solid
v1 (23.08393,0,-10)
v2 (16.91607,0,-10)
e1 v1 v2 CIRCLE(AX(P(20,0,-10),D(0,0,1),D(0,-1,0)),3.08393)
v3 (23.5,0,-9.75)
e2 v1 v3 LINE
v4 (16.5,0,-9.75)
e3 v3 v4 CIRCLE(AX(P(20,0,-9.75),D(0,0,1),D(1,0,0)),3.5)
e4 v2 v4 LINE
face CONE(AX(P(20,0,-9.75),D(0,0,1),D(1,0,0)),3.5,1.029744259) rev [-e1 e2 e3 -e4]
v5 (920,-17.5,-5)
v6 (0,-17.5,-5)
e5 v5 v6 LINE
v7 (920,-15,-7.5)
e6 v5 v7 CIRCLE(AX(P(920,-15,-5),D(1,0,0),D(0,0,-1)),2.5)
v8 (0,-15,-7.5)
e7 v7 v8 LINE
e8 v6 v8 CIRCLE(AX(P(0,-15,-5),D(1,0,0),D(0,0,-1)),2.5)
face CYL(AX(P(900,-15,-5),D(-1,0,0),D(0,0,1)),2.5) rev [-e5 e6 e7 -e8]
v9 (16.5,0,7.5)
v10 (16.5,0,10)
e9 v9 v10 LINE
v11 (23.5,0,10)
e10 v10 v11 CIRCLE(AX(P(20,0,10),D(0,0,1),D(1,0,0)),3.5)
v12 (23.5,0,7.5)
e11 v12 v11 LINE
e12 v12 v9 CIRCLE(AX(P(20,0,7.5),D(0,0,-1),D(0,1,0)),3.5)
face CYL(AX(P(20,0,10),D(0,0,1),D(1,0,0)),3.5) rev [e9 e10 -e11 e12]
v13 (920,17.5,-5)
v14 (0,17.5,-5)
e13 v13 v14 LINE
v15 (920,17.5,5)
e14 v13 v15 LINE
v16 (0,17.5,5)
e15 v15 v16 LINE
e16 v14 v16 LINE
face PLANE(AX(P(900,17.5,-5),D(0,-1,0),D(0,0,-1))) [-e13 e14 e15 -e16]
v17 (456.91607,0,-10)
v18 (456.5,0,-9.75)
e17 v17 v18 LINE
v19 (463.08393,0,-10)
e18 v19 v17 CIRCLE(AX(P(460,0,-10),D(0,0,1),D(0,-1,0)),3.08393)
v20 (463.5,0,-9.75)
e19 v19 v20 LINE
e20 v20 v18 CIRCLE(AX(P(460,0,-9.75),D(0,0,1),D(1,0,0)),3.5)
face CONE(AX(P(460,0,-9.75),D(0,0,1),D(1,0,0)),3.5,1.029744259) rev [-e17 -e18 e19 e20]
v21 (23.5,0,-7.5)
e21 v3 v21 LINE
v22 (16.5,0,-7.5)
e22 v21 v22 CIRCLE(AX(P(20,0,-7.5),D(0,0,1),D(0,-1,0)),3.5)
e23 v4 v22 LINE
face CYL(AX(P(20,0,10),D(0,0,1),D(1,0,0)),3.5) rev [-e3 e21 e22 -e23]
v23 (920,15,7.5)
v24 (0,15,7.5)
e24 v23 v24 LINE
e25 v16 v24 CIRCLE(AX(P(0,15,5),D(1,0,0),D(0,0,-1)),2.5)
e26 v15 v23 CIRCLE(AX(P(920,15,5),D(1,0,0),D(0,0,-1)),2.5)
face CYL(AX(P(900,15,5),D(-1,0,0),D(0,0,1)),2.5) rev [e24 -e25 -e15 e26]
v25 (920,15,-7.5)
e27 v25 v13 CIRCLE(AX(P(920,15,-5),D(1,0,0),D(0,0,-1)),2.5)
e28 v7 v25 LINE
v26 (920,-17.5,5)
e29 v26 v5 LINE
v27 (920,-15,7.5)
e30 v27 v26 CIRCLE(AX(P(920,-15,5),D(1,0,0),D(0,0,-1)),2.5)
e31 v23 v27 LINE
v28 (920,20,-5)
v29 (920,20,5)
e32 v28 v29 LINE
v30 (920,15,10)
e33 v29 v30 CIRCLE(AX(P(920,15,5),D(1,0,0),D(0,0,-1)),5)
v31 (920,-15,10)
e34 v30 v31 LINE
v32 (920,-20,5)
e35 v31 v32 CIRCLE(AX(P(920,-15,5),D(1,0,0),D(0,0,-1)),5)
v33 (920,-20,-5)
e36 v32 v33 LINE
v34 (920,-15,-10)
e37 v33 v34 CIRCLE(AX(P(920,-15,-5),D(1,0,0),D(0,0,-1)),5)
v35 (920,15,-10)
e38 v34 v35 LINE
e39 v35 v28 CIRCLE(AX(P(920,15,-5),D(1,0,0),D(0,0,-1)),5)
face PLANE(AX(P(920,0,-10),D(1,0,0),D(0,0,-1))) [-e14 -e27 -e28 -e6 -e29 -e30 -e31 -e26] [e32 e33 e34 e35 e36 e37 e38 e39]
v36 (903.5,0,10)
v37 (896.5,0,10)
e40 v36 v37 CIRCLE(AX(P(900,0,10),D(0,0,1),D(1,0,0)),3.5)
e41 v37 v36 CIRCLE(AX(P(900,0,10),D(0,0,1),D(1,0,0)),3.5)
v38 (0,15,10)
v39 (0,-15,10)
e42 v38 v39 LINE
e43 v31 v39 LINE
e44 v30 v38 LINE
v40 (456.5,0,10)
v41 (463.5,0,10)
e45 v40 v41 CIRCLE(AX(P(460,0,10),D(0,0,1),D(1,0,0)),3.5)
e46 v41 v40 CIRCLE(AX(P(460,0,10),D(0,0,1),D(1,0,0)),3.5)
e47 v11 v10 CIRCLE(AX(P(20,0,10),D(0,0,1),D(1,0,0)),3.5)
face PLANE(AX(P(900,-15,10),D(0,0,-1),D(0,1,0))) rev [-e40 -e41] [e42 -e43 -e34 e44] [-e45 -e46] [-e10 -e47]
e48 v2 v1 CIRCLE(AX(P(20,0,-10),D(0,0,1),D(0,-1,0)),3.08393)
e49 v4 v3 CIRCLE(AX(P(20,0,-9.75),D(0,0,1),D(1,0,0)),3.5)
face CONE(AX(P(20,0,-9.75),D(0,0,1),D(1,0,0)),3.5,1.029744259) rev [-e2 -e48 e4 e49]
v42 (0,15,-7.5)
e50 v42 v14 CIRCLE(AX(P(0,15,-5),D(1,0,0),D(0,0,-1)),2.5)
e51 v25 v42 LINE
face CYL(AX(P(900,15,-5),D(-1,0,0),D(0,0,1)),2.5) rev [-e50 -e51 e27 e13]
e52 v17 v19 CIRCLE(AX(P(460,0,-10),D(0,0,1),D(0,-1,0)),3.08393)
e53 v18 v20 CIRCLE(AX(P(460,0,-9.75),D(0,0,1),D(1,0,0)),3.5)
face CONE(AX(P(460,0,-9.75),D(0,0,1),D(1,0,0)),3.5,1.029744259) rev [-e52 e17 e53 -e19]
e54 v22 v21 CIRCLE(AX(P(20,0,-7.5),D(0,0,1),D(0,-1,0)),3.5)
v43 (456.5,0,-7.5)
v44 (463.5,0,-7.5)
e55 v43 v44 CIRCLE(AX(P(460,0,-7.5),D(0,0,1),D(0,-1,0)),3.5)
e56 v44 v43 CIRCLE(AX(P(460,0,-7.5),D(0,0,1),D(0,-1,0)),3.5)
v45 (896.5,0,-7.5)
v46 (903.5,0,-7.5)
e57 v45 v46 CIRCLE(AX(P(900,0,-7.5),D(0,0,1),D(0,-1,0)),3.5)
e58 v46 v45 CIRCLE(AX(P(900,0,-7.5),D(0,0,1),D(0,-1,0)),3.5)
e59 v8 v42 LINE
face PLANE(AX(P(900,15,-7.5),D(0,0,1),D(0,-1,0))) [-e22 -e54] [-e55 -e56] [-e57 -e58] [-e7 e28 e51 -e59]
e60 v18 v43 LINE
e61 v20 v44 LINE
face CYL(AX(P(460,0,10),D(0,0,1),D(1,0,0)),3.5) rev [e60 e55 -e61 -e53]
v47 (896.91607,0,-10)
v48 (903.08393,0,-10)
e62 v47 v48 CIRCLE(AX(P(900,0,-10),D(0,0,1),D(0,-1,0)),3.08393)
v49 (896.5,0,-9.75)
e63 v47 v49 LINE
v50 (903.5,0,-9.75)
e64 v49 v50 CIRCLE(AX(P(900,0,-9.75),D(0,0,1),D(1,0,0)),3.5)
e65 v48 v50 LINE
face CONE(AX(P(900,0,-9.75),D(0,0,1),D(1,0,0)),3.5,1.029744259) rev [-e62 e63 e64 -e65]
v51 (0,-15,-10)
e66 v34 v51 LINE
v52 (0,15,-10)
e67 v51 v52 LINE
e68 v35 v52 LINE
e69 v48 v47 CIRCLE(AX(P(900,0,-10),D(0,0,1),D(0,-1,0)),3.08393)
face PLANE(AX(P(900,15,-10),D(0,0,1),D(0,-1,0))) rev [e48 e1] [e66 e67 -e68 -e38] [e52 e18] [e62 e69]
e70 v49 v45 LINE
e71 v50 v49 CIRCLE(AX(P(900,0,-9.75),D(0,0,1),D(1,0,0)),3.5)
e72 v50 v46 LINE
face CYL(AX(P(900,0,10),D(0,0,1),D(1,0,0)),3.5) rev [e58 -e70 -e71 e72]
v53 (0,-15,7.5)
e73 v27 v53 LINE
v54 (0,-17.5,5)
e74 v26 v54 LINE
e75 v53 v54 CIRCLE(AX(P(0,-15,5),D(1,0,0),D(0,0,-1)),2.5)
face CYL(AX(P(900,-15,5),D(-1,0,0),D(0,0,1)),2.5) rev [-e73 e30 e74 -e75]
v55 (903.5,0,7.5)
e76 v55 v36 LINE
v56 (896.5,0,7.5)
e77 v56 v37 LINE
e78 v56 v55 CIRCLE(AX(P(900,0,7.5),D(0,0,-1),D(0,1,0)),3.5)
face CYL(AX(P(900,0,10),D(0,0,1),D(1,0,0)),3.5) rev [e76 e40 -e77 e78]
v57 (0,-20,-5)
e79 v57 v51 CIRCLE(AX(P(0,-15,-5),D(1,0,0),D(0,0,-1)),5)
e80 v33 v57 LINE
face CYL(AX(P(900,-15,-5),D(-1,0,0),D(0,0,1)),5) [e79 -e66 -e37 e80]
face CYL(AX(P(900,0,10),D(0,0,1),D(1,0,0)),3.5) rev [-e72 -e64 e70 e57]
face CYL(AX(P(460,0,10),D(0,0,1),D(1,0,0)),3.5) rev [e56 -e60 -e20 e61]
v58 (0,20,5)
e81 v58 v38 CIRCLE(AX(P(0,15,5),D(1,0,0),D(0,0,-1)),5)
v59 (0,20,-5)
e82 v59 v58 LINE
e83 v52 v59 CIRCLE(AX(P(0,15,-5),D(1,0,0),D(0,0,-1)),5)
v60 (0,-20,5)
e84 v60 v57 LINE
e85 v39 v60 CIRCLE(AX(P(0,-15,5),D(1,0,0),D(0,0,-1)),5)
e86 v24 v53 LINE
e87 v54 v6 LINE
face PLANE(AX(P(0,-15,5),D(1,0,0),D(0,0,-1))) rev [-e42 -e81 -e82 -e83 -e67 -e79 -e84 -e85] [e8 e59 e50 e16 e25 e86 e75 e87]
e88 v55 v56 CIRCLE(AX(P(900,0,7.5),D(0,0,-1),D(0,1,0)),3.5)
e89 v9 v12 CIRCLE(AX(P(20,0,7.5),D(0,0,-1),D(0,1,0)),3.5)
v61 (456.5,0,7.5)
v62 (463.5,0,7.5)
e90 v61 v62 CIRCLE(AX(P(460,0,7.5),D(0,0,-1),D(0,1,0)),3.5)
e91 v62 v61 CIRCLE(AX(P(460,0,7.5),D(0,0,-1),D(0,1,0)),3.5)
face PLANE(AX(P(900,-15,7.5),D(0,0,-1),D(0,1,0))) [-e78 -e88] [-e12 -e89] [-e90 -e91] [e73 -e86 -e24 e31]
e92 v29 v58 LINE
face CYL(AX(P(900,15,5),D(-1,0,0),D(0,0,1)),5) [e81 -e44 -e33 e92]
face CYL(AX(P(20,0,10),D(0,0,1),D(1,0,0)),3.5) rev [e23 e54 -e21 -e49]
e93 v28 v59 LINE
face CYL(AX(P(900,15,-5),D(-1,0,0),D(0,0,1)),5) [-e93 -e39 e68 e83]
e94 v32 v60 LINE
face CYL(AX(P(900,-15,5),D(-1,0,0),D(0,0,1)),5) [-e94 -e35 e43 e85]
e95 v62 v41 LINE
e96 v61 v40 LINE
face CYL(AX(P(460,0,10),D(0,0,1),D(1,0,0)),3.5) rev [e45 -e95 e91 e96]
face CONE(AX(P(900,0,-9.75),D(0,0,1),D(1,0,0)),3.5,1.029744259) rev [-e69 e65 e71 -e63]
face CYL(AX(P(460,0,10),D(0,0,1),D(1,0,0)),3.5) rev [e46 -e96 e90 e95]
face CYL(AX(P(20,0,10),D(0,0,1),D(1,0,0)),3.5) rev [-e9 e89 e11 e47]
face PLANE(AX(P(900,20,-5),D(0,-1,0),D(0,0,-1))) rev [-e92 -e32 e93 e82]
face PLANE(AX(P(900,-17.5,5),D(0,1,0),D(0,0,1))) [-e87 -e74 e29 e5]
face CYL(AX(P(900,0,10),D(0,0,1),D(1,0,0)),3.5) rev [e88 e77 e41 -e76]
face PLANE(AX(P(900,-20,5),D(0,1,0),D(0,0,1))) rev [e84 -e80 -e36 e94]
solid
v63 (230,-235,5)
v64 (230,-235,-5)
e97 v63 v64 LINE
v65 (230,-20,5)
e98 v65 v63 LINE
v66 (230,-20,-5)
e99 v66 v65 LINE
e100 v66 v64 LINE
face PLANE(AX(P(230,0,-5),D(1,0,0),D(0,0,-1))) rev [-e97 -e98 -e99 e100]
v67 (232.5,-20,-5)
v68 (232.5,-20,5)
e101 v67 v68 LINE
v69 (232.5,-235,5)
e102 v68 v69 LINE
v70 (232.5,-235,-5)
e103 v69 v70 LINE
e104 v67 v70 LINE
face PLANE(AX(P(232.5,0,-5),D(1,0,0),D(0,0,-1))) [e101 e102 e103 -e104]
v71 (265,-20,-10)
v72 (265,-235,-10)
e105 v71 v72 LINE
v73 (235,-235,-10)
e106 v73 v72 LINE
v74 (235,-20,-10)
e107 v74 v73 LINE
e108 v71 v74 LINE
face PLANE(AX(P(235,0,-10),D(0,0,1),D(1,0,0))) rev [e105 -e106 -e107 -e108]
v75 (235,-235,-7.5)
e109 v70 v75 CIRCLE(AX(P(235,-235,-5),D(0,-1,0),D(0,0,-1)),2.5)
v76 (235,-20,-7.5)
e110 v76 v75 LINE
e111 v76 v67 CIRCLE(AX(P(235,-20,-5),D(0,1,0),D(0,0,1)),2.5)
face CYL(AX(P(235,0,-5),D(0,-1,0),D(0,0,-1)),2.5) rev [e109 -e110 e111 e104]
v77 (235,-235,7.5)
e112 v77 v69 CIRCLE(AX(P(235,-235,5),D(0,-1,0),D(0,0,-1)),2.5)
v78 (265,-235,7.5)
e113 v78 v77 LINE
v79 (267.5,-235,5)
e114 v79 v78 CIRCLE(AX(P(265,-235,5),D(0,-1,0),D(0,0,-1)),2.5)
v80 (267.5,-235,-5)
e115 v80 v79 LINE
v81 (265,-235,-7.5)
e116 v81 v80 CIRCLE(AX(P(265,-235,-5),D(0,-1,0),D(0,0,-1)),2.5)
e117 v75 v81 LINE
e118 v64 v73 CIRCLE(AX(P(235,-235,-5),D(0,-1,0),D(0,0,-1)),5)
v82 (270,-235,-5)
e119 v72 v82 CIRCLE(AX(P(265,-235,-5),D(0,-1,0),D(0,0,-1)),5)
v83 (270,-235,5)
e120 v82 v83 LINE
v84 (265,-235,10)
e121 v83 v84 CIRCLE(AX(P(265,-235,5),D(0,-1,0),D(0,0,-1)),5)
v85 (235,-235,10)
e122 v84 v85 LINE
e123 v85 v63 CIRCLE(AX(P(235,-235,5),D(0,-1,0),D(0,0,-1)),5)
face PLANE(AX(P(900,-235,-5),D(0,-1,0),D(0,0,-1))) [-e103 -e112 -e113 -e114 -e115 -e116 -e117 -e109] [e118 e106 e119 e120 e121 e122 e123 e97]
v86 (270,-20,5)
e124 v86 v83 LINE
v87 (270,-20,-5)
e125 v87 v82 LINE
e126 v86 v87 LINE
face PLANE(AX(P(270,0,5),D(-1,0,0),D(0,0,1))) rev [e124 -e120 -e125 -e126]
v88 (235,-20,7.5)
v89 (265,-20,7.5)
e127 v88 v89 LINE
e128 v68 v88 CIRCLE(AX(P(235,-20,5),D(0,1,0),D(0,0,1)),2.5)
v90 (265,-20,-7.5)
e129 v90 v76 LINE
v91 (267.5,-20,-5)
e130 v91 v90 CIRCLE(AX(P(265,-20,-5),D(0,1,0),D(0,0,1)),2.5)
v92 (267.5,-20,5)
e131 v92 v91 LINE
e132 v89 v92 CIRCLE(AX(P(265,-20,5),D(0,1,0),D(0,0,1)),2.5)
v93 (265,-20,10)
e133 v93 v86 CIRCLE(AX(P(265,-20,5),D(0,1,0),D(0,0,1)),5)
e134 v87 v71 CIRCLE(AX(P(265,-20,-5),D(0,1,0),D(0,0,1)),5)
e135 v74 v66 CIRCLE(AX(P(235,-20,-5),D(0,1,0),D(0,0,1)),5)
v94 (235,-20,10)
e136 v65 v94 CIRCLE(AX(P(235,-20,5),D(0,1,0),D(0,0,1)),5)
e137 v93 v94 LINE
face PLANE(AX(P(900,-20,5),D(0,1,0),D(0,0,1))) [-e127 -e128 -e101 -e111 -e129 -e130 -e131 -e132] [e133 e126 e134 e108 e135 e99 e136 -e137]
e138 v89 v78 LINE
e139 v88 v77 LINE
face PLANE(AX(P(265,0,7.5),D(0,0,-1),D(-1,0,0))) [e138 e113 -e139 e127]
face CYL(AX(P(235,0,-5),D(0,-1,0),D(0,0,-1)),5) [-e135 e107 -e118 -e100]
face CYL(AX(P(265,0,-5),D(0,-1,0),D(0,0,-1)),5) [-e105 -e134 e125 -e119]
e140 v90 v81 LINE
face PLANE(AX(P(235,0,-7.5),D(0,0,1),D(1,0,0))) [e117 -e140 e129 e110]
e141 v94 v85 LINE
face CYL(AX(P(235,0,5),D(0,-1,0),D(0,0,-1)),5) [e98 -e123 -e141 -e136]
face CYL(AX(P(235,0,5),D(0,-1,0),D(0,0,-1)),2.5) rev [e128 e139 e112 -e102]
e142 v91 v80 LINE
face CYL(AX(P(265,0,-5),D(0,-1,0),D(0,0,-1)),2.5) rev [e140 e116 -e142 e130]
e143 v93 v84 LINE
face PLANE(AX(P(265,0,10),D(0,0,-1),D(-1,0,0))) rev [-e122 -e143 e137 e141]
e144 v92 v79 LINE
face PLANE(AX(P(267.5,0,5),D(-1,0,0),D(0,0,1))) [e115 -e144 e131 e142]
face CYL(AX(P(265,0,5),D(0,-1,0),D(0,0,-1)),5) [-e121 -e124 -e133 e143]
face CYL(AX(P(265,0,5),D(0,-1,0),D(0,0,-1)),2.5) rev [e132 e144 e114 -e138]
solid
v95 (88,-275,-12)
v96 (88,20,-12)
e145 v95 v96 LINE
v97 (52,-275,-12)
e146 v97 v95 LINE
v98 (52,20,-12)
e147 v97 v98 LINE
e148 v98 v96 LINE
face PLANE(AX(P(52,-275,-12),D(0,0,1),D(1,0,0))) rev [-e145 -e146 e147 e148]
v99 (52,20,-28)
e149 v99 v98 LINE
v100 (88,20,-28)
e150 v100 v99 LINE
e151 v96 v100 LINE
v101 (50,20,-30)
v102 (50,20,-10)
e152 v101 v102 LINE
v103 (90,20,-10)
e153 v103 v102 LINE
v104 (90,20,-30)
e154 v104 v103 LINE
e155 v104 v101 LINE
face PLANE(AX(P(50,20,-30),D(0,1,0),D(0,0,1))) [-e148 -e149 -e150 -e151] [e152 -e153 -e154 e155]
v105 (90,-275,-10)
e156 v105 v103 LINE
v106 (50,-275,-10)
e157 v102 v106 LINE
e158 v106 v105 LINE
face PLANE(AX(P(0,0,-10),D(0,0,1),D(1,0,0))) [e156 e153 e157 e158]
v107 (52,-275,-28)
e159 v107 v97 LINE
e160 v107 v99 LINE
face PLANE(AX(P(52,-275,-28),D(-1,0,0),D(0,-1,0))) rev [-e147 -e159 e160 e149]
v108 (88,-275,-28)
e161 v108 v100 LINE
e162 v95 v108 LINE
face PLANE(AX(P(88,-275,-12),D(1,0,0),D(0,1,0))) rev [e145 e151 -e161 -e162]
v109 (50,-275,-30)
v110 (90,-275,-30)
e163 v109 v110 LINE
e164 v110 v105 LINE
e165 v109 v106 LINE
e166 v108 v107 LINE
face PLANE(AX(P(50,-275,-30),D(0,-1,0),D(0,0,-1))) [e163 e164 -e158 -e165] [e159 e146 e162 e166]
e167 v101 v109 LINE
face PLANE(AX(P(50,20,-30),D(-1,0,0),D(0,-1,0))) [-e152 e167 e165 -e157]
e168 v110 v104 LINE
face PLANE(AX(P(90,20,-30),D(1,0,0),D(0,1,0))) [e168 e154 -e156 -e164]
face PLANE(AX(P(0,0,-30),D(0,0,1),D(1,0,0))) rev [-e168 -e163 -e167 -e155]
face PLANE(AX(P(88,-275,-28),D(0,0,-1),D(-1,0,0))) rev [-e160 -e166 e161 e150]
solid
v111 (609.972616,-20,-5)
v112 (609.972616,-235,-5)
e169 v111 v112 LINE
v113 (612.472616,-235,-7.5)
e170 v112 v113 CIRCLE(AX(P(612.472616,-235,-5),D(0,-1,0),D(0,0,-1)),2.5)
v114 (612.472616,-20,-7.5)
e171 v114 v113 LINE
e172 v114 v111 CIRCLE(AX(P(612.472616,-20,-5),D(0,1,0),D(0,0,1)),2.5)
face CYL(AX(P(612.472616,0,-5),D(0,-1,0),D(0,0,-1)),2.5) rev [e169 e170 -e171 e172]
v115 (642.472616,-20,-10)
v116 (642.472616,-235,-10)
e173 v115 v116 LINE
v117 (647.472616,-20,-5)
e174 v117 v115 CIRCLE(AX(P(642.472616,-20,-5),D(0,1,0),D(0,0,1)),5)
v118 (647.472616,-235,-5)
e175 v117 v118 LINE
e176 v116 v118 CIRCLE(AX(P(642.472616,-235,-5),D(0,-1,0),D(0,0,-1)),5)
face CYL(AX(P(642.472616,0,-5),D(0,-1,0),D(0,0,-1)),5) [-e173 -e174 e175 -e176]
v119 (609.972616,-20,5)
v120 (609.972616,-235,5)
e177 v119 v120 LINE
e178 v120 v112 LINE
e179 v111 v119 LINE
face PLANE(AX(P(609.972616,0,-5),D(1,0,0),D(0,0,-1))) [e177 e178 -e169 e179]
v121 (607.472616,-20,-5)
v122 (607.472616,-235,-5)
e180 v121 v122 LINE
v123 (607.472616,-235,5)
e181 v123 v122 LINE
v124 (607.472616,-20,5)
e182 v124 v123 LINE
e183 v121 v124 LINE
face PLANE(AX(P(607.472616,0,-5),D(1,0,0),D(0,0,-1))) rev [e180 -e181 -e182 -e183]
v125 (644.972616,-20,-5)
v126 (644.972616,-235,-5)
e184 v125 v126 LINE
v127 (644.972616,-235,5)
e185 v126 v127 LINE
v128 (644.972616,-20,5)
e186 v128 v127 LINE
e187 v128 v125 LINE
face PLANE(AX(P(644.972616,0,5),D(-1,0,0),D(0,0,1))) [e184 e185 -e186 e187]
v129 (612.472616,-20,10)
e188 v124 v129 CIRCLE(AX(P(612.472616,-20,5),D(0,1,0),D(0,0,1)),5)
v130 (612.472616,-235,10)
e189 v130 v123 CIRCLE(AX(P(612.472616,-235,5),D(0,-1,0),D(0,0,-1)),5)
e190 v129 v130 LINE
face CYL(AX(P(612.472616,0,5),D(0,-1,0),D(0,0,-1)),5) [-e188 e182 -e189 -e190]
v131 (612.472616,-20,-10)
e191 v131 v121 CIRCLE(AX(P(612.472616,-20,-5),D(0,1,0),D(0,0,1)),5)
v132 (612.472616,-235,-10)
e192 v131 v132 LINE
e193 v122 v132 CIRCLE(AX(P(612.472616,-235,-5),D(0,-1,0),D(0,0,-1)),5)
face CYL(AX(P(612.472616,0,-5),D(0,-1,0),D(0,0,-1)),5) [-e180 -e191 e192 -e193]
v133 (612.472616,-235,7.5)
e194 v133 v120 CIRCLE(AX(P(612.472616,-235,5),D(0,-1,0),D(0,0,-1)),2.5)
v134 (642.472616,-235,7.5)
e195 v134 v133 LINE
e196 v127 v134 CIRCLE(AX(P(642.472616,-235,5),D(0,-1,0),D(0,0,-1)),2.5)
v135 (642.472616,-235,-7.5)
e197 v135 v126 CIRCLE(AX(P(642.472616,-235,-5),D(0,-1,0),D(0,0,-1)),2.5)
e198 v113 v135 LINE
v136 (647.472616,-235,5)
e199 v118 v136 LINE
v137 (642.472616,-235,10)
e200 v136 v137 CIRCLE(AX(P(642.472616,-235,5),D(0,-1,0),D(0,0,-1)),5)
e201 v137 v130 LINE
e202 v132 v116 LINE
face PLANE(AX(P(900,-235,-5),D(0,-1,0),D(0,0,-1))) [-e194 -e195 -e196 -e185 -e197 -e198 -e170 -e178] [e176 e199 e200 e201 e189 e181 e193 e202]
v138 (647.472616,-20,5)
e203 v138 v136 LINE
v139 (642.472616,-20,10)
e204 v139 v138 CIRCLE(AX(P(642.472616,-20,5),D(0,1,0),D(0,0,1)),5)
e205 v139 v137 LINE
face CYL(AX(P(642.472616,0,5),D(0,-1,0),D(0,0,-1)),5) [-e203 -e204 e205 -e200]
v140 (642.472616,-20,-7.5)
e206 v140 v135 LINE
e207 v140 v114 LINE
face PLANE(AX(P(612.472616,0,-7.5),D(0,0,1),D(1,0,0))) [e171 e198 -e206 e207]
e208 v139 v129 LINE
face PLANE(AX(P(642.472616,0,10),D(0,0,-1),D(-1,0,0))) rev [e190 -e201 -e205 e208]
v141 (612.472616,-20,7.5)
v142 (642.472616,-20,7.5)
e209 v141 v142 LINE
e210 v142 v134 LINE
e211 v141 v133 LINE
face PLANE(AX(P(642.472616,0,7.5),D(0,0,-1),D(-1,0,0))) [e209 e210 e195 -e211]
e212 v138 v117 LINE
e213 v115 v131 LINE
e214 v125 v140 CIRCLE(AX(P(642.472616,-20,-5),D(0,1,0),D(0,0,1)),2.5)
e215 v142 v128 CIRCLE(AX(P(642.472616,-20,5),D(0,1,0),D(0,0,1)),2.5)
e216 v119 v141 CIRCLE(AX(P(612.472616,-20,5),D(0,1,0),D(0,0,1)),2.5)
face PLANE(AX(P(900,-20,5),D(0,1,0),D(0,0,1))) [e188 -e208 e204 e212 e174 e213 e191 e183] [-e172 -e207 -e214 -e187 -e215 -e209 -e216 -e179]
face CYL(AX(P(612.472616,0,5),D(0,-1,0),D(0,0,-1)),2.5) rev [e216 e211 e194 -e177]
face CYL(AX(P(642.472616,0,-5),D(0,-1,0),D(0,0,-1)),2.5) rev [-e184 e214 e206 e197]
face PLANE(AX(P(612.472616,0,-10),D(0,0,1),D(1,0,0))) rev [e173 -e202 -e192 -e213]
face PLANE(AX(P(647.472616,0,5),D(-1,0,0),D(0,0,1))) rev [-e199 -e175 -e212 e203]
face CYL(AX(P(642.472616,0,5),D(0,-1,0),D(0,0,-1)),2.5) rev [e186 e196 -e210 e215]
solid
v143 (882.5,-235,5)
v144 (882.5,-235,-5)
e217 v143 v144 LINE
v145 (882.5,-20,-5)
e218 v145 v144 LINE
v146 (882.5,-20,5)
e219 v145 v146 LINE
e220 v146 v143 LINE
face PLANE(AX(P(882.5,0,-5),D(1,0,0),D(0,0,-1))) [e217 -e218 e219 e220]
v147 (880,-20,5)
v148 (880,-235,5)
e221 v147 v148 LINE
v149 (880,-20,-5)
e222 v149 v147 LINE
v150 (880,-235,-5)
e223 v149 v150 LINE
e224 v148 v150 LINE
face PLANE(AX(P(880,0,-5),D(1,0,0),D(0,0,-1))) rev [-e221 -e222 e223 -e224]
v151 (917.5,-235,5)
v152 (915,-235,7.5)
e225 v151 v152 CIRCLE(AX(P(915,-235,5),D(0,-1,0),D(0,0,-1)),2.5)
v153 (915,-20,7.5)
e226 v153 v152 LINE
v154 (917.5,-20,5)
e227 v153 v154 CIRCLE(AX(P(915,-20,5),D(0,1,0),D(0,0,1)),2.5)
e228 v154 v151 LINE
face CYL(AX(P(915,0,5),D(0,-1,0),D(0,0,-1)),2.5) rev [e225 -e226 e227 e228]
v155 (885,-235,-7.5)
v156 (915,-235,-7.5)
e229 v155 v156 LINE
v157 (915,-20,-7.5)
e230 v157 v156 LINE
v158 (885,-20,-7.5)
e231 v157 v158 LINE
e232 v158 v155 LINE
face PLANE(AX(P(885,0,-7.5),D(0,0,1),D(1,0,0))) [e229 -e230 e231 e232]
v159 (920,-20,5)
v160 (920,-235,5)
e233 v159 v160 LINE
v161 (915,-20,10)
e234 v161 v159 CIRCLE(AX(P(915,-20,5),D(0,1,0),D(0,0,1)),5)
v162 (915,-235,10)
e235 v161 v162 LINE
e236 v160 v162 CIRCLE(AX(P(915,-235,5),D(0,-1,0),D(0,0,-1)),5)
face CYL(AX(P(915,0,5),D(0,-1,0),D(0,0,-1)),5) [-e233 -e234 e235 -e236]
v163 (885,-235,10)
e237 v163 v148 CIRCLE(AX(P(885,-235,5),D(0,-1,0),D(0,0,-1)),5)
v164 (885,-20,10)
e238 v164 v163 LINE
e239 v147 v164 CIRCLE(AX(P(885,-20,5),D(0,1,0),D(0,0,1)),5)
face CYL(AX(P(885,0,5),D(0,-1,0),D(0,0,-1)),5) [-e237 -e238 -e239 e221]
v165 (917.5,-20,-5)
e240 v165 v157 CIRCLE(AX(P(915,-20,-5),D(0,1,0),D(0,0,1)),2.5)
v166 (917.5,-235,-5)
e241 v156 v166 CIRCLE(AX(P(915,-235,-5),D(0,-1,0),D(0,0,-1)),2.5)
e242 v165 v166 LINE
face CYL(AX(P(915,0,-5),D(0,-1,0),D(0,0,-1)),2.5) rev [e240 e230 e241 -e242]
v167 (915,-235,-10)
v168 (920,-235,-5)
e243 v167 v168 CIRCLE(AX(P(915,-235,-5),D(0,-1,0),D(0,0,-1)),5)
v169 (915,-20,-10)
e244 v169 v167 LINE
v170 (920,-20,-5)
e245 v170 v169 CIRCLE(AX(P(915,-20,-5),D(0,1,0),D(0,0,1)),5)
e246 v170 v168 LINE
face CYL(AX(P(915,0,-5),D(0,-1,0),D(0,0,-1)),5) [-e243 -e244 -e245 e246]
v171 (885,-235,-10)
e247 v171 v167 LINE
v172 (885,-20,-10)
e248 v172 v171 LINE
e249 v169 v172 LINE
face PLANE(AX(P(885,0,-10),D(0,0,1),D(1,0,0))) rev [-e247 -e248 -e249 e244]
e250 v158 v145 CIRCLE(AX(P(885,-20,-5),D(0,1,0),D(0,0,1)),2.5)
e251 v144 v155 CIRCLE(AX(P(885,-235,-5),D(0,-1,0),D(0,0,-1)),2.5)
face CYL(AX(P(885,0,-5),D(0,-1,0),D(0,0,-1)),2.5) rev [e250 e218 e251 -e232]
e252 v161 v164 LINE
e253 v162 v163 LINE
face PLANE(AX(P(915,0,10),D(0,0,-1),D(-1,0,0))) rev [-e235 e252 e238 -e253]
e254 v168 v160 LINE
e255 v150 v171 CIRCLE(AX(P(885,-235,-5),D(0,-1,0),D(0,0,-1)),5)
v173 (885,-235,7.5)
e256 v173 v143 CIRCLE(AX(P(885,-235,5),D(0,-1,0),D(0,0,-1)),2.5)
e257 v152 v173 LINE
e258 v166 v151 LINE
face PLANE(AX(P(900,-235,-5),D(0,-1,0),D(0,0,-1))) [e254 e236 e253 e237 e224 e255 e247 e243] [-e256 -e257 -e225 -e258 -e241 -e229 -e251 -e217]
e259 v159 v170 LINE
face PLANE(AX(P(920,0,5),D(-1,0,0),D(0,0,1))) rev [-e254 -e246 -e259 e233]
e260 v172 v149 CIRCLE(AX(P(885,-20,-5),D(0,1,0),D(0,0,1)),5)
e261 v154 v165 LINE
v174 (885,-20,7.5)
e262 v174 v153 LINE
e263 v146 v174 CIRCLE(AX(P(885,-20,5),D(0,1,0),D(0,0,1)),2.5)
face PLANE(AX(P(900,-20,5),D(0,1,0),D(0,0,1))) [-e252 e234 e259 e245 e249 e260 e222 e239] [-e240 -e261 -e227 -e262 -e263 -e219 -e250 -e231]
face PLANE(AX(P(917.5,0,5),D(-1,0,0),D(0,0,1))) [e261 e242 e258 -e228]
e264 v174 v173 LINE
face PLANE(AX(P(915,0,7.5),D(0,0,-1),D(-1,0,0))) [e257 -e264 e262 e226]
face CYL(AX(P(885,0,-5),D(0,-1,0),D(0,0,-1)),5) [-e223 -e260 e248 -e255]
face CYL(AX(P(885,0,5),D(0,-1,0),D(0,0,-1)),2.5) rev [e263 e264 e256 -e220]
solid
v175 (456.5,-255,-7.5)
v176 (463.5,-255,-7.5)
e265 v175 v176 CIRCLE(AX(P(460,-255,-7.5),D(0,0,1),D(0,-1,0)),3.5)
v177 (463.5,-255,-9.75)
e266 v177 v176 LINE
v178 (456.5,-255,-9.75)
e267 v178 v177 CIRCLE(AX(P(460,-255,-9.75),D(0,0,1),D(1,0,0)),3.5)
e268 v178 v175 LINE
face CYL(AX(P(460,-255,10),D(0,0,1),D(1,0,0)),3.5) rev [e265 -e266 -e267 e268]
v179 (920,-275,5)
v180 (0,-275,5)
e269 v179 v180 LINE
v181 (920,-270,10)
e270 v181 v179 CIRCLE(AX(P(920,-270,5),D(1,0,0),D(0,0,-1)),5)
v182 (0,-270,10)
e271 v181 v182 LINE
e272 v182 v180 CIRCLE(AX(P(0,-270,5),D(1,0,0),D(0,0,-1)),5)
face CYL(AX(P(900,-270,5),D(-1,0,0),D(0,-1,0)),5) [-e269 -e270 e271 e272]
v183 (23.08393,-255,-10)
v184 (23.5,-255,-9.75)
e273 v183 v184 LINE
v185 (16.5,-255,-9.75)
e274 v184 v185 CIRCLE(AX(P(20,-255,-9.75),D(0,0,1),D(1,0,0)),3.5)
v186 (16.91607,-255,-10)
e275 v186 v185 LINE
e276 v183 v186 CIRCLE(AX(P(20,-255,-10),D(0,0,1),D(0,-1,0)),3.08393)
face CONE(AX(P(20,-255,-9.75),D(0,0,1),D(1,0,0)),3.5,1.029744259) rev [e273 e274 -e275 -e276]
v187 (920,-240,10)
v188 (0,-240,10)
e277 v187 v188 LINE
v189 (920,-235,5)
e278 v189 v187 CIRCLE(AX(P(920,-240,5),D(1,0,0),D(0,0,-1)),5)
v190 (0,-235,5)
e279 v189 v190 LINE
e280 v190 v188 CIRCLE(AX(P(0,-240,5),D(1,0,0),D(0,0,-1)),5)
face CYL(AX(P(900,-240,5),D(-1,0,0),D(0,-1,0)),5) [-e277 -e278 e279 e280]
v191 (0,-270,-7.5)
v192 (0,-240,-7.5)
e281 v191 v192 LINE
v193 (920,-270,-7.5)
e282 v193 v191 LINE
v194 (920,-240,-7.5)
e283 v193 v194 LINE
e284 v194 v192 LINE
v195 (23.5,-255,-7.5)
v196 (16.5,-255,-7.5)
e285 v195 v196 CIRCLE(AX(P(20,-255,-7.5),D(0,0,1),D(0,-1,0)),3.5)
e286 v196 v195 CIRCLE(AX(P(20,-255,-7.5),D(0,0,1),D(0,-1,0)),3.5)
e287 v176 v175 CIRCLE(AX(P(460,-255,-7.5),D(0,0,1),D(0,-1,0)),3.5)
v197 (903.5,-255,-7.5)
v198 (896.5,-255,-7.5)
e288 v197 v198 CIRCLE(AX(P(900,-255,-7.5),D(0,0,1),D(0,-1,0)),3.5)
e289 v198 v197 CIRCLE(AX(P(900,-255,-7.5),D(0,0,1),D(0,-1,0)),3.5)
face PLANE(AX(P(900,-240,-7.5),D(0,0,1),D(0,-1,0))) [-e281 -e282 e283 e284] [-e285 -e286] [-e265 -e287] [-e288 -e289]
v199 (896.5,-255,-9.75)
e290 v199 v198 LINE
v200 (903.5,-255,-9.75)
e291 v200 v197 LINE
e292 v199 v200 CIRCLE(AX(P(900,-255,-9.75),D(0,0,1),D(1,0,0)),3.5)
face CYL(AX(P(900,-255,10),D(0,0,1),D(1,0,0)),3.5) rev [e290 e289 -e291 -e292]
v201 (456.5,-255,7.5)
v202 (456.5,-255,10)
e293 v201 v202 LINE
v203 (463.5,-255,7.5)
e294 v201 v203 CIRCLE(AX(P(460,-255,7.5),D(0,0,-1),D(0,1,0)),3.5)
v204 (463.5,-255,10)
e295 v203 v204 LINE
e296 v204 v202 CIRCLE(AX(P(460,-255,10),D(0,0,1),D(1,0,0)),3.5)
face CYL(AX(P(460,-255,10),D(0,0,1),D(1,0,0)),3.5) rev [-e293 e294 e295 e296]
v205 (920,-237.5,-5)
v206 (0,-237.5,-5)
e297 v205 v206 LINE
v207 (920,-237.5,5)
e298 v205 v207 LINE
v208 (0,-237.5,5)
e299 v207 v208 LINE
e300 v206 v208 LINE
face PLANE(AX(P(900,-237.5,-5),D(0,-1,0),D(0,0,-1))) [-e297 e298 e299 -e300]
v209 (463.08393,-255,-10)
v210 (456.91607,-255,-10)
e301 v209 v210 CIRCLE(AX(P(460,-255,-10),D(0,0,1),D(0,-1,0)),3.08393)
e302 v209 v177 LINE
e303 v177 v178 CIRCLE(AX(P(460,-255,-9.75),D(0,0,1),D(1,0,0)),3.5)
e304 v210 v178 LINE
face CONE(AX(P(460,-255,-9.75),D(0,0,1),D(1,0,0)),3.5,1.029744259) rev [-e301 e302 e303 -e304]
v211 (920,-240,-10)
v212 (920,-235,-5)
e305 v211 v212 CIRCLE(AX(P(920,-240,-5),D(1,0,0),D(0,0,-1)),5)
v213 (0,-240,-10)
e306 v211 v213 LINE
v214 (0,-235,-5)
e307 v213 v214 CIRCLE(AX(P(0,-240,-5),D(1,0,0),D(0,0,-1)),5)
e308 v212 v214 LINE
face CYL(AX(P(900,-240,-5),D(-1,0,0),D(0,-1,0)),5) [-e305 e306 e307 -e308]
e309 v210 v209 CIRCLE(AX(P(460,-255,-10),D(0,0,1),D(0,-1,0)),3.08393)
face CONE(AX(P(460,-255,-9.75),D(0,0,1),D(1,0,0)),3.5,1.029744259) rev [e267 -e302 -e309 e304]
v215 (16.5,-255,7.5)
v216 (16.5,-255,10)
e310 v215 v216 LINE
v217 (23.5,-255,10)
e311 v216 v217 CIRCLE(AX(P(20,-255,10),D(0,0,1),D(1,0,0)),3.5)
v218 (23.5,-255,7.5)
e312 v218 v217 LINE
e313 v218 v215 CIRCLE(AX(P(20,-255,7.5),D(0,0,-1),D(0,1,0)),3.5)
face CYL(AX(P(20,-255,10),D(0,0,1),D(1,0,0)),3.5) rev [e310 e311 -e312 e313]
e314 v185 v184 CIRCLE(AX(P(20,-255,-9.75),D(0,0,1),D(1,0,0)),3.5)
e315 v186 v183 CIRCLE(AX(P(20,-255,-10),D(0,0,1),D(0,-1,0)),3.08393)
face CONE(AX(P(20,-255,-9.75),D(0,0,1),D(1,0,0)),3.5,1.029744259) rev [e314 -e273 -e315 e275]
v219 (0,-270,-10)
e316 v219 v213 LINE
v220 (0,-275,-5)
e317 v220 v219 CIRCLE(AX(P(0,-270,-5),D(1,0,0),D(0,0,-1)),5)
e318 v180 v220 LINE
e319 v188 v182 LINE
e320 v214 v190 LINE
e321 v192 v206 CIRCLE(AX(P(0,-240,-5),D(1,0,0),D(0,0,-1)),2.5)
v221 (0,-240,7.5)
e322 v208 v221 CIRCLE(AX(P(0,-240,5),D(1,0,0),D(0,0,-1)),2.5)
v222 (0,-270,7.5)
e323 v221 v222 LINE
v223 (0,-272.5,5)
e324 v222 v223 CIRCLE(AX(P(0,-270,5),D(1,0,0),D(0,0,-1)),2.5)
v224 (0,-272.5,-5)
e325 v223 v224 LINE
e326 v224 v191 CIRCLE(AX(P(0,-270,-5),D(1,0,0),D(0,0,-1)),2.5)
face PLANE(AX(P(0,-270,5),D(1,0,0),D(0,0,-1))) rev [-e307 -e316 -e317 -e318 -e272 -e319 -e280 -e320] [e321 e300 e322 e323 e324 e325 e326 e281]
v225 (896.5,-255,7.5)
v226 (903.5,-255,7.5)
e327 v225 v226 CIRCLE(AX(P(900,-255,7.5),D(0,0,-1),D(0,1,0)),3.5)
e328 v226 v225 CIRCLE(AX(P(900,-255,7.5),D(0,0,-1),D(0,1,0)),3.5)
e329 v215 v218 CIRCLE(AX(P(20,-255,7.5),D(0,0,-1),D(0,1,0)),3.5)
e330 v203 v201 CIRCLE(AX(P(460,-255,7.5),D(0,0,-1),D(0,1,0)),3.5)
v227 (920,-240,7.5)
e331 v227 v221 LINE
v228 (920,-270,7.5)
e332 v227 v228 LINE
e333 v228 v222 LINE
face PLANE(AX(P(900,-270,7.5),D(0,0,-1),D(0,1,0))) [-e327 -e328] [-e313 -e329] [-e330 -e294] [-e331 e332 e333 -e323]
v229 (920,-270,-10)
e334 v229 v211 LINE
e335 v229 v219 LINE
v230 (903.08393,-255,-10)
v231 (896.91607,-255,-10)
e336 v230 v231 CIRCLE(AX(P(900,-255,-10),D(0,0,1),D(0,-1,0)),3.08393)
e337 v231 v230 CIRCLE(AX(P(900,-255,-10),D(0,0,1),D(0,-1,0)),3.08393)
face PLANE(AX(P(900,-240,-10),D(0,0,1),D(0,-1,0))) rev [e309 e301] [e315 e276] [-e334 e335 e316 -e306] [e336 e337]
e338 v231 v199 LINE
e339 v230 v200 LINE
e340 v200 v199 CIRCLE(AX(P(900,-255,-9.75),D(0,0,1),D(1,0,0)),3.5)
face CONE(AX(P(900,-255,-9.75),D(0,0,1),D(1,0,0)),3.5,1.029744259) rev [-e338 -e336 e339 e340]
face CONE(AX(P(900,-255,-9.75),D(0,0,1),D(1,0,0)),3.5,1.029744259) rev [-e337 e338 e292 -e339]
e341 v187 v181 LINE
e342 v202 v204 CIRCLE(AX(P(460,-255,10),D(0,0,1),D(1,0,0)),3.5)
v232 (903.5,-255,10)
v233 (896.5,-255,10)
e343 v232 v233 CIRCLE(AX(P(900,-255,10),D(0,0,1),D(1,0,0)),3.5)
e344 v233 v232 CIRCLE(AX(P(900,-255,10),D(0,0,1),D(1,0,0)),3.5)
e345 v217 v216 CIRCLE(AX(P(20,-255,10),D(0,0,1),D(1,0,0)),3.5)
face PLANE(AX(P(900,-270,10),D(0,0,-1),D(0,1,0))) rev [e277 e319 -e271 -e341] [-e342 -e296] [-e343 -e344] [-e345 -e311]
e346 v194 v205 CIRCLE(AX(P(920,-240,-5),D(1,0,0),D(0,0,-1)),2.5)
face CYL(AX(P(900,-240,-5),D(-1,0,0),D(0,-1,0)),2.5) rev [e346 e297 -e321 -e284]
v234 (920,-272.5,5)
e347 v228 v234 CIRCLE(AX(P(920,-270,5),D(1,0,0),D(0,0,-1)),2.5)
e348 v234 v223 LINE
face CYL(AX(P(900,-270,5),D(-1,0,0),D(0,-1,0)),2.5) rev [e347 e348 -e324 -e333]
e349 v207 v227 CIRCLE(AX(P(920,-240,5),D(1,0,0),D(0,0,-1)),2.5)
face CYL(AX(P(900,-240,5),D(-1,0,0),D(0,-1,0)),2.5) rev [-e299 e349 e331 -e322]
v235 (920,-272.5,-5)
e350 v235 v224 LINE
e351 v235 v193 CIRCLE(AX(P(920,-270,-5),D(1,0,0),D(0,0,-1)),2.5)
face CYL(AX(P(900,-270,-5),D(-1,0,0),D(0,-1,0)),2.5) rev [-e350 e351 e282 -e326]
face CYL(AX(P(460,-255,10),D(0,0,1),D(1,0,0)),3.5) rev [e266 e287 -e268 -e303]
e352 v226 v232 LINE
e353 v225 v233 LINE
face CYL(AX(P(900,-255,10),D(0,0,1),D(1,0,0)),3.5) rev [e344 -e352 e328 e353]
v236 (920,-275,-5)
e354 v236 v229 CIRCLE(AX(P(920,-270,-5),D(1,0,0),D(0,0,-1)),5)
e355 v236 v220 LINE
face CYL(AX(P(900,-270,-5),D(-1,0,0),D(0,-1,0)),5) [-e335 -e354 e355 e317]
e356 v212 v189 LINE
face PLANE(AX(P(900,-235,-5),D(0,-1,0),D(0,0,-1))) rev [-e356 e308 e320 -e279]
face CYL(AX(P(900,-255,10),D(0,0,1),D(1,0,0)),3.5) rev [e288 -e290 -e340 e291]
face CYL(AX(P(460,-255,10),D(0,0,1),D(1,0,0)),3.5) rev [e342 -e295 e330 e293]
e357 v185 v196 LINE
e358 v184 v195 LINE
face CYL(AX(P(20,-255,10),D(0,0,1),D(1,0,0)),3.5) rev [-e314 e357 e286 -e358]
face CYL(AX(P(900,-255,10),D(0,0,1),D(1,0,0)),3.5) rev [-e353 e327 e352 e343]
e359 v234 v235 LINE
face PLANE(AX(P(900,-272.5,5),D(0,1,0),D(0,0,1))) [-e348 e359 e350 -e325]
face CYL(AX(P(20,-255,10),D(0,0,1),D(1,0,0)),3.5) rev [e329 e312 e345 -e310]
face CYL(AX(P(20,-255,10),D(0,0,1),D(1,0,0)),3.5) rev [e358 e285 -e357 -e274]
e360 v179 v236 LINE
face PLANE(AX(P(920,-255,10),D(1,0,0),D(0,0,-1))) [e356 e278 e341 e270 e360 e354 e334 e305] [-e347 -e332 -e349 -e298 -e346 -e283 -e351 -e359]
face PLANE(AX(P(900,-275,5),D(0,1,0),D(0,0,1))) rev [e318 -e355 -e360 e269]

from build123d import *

# Parameters (mm, degrees)
RECT_TUBE_40X20X2_5_1_DEPTH   = 920
RECT_TUBE_40X20X2_5_1_2_DEPTH = 920
RECT_TUBE_40X20X2_5_1_3_DEPTH = 257
RECT_TUBE_40X20X2_5_1_4_DEPTH = 257
RECT_TUBE_40X20X2_5_1_5_DEPTH = 257
M6_CLEARANCE_HOLE1_AT_2_COUNT = 2
M6_CLEARANCE_HOLE1_AT_2_PITCH = 255
M6_CLEARANCE_HOLE1_AT_3_COUNT = 2
M6_CLEARANCE_HOLE1_AT_3_PITCH = 508.551865595
M6_CLEARANCE_HOLE1_AT_4_COUNT = 2
M6_CLEARANCE_HOLE1_AT_4_PITCH = 440
M6_CLEARANCE_HOLE1_AT_5_COUNT = 2
M6_CLEARANCE_HOLE1_AT_5_PITCH = 916.201397074
M6_CLEARANCE_HOLE1_AT_6_COUNT = 2
M6_CLEARANCE_HOLE1_AT_6_PITCH = 880
SKETCH7_W                     = 40
SKETCH7_H                     = 295
BOSS_EXTRUDE1_DEPTH           = 20
SKETCH8_W                     = 36
SKETCH8_H                     = 16
CUT_EXTRUDE1_DEPTH            = 967.604883083


with BuildPart() as part:
    # Sketch1 → Rect Tube 40X20X2.5(1) (new body)
    with BuildSketch(Plane(origin=(0, 0, 0), x_dir=(0, 0, 1), z_dir=(1, 0, 0))):
        with BuildLine():
            Line((-5, -20), (5, -20))
            ThreePointArc((5, -20), (8.535533906, -18.535533906), (10, -15))
            Line((10, -15), (10, 15))
            ThreePointArc((10, 15), (8.535533906, 18.535533906), (5, 20))
            Line((5, 20), (-5, 20))
            ThreePointArc((-5, 20), (-8.535533906, 18.535533906), (-10, 15))
            Line((-10, 15), (-10, -15))
            ThreePointArc((-10, -15), (-8.535533906, -18.535533906), (-5, -20))
        make_face()
        with BuildLine():
            Line((-5, -17.5), (5, -17.5))
            ThreePointArc((5, -17.5), (6.767766953, -16.767766953), (7.5, -15))
            Line((7.5, -15), (7.5, 15))
            ThreePointArc((7.5, 15), (6.767766953, 16.767766953), (5, 17.5))
            Line((5, 17.5), (-5, 17.5))
            ThreePointArc((-5, 17.5), (-6.767766953, 16.767766953), (-7.5, 15))
            Line((-7.5, 15), (-7.5, -15))
            ThreePointArc((-7.5, -15), (-6.767766953, -16.767766953), (-5, -17.5))
        make_face(mode=Mode.SUBTRACT)
    extrude(amount=RECT_TUBE_40X20X2_5_1_DEPTH)


with BuildPart() as body_2:
    # Sketch1 on segment 2 (carried to segment 2) → Rect Tube 40X20X2.5_1 2 (new body)
    with BuildSketch(Plane(origin=(0, -255, 0), x_dir=(0, 0, 1), z_dir=(1, 0, 0))):
        with BuildLine():
            Line((-5, -20), (5, -20))
            ThreePointArc((5, -20), (8.535533906, -18.535533906), (10, -15))
            Line((10, -15), (10, 15))
            ThreePointArc((10, 15), (8.535533906, 18.535533906), (5, 20))
            Line((5, 20), (-5, 20))
            ThreePointArc((-5, 20), (-8.535533906, 18.535533906), (-10, 15))
            Line((-10, 15), (-10, -15))
            ThreePointArc((-10, -15), (-8.535533906, -18.535533906), (-5, -20))
        make_face()
        with BuildLine():
            Line((-5, -17.5), (5, -17.5))
            ThreePointArc((5, -17.5), (6.767766953, -16.767766953), (7.5, -15))
            Line((7.5, -15), (7.5, 15))
            ThreePointArc((7.5, 15), (6.767766953, 16.767766953), (5, 17.5))
            Line((5, 17.5), (-5, 17.5))
            ThreePointArc((-5, 17.5), (-6.767766953, 16.767766953), (-7.5, 15))
            Line((-7.5, 15), (-7.5, -15))
            ThreePointArc((-7.5, -15), (-6.767766953, -16.767766953), (-5, -17.5))
        make_face(mode=Mode.SUBTRACT)
    extrude(amount=RECT_TUBE_40X20X2_5_1_2_DEPTH)

    # Sketch4 → M6 Clearance Hole1 (revolve, cut)
    with BuildSketch(Plane(origin=(20, -255, 10), x_dir=(0, -1, 0), z_dir=(1, 0, 0))):
        Polygon((0, 0), (0, 21.853012167), (3.5, 19.75), (3.5, 0), align=None)
    m6_clearance_hole1 = revolve(axis=Axis((20, -255, 16.35), (0, 0, -1)), mode=Mode.SUBTRACT)

    # M6 Clearance Hole1 at 4: M6 Clearance Hole1 ×2
    with Locations(*[(i * M6_CLEARANCE_HOLE1_AT_4_PITCH, 0, 0) for i in range(1, M6_CLEARANCE_HOLE1_AT_4_COUNT)]):
        add(m6_clearance_hole1, mode=Mode.SUBTRACT)

    # M6 Clearance Hole1 at 6: M6 Clearance Hole1 ×2
    with Locations(*[(i * M6_CLEARANCE_HOLE1_AT_6_PITCH, 0, 0) for i in range(1, M6_CLEARANCE_HOLE1_AT_6_COUNT)]):
        add(m6_clearance_hole1, mode=Mode.SUBTRACT)


with BuildPart() as body_3:
    # Sketch1 on segment 3 (carried to segment 3) → Rect Tube 40X20X2.5_1 3 (new body)
    with BuildSketch(Plane(origin=(900, 1, 0), x_dir=(0, 0, 1), z_dir=(0, -1, 0))):
        with BuildLine():
            Line((-5, -20), (5, -20))
            ThreePointArc((5, -20), (8.535533906, -18.535533906), (10, -15))
            Line((10, -15), (10, 15))
            ThreePointArc((10, 15), (8.535533906, 18.535533906), (5, 20))
            Line((5, 20), (-5, 20))
            ThreePointArc((-5, 20), (-8.535533906, 18.535533906), (-10, 15))
            Line((-10, 15), (-10, -15))
            ThreePointArc((-10, -15), (-8.535533906, -18.535533906), (-5, -20))
        make_face()
        with BuildLine():
            Line((-5, -17.5), (5, -17.5))
            ThreePointArc((5, -17.5), (6.767766953, -16.767766953), (7.5, -15))
            Line((7.5, -15), (7.5, 15))
            ThreePointArc((7.5, 15), (6.767766953, 16.767766953), (5, 17.5))
            Line((5, 17.5), (-5, 17.5))
            ThreePointArc((-5, 17.5), (-6.767766953, 16.767766953), (-7.5, 15))
            Line((-7.5, 15), (-7.5, -15))
            ThreePointArc((-7.5, -15), (-6.767766953, -16.767766953), (-5, -17.5))
        make_face(mode=Mode.SUBTRACT)
    extrude(amount=RECT_TUBE_40X20X2_5_1_3_DEPTH)

    # Rect Tube 40X20X2.5_1 3 end butt 1
    split(bisect_by=Plane(origin=(900, -20, 0), x_dir=(1, 0, 0), z_dir=(0, -1, 0)), keep=Keep.TOP)

    # Rect Tube 40X20X2.5_1 3 end butt 2
    split(bisect_by=Plane(origin=(900, -235, 0), x_dir=(-1, 0, 0), z_dir=(0, 1, 0)), keep=Keep.TOP)


with BuildPart() as body_4:
    # Sketch1 on segment 4 (carried to segment 4) → Rect Tube 40X20X2.5_1 4 (new body)
    with BuildSketch(Plane(origin=(250, 1, 0), x_dir=(0, 0, 1), z_dir=(0, -1, 0))):
        with BuildLine():
            Line((-5, -20), (5, -20))
            ThreePointArc((5, -20), (8.535533906, -18.535533906), (10, -15))
            Line((10, -15), (10, 15))
            ThreePointArc((10, 15), (8.535533906, 18.535533906), (5, 20))
            Line((5, 20), (-5, 20))
            ThreePointArc((-5, 20), (-8.535533906, 18.535533906), (-10, 15))
            Line((-10, 15), (-10, -15))
            ThreePointArc((-10, -15), (-8.535533906, -18.535533906), (-5, -20))
        make_face()
        with BuildLine():
            Line((-5, -17.5), (5, -17.5))
            ThreePointArc((5, -17.5), (6.767766953, -16.767766953), (7.5, -15))
            Line((7.5, -15), (7.5, 15))
            ThreePointArc((7.5, 15), (6.767766953, 16.767766953), (5, 17.5))
            Line((5, 17.5), (-5, 17.5))
            ThreePointArc((-5, 17.5), (-6.767766953, 16.767766953), (-7.5, 15))
            Line((-7.5, 15), (-7.5, -15))
            ThreePointArc((-7.5, -15), (-6.767766953, -16.767766953), (-5, -17.5))
        make_face(mode=Mode.SUBTRACT)
    extrude(amount=RECT_TUBE_40X20X2_5_1_4_DEPTH)

    # Rect Tube 40X20X2.5_1 4 end butt 1
    split(bisect_by=Plane(origin=(250, -20, 0), x_dir=(1, 0, 0), z_dir=(0, -1, 0)), keep=Keep.TOP)

    # Rect Tube 40X20X2.5_1 4 end butt 2
    split(bisect_by=Plane(origin=(250, -235, 0), x_dir=(-1, 0, 0), z_dir=(0, 1, 0)), keep=Keep.TOP)


with BuildPart() as body_5:
    # Sketch1 on segment 5 (carried to segment 5) → Rect Tube 40X20X2.5_1 5 (new body)
    with BuildSketch(Plane(origin=(627.472616431, 1, 0), x_dir=(0, 0, 1), z_dir=(0, -1, 0))):
        with BuildLine():
            Line((-5, -20), (5, -20))
            ThreePointArc((5, -20), (8.535533906, -18.535533906), (10, -15))
            Line((10, -15), (10, 15))
            ThreePointArc((10, 15), (8.535533906, 18.535533906), (5, 20))
            Line((5, 20), (-5, 20))
            ThreePointArc((-5, 20), (-8.535533906, 18.535533906), (-10, 15))
            Line((-10, 15), (-10, -15))
            ThreePointArc((-10, -15), (-8.535533906, -18.535533906), (-5, -20))
        make_face()
        with BuildLine():
            Line((-5, -17.5), (5, -17.5))
            ThreePointArc((5, -17.5), (6.767766953, -16.767766953), (7.5, -15))
            Line((7.5, -15), (7.5, 15))
            ThreePointArc((7.5, 15), (6.767766953, 16.767766953), (5, 17.5))
            Line((5, 17.5), (-5, 17.5))
            ThreePointArc((-5, 17.5), (-6.767766953, 16.767766953), (-7.5, 15))
            Line((-7.5, 15), (-7.5, -15))
            ThreePointArc((-7.5, -15), (-6.767766953, -16.767766953), (-5, -17.5))
        make_face(mode=Mode.SUBTRACT)
    extrude(amount=RECT_TUBE_40X20X2_5_1_5_DEPTH)

    # Rect Tube 40X20X2.5_1 5 end butt 1
    split(bisect_by=Plane(origin=(627.472616431, -20, 0), x_dir=(1, 0, 0), z_dir=(0, -1, 0)), keep=Keep.TOP)

    # Rect Tube 40X20X2.5_1 5 end butt 2
    split(bisect_by=Plane(origin=(627.472616431, -235, 0), x_dir=(-1, 0, 0), z_dir=(0, 1, 0)), keep=Keep.TOP)


with BuildPart() as part_1:
    add(part.part)

    # M6 Clearance Hole1 at 2: M6 Clearance Hole1 ×2
    with Locations(*[(0, i * M6_CLEARANCE_HOLE1_AT_2_PITCH, 0) for i in range(1, M6_CLEARANCE_HOLE1_AT_2_COUNT)]):
        add(m6_clearance_hole1, mode=Mode.SUBTRACT)

    # M6 Clearance Hole1 at 3: M6 Clearance Hole1 ×2
    with Locations(*[Vector(0.8652018206350236, 0.5014237824134796, 0) * (i * M6_CLEARANCE_HOLE1_AT_3_PITCH) for i in range(1, M6_CLEARANCE_HOLE1_AT_3_COUNT)]):
        add(m6_clearance_hole1, mode=Mode.SUBTRACT)

    # M6 Clearance Hole1 at 5: M6 Clearance Hole1 ×2
    with Locations(*[Vector(0.9604875116001456, 0.2783230857477695, 0) * (i * M6_CLEARANCE_HOLE1_AT_5_PITCH) for i in range(1, M6_CLEARANCE_HOLE1_AT_5_COUNT)]):
        add(m6_clearance_hole1, mode=Mode.SUBTRACT)


with BuildPart() as body_6:
    # Sketch7 → Boss-Extrude1 (new body)
    with BuildSketch(Plane.XY.offset(-10)):
        with Locations((70, -127.5)):
            Rectangle(SKETCH7_W, SKETCH7_H)
    extrude(amount=-BOSS_EXTRUDE1_DEPTH)

    # Sketch8 → Cut-Extrude1 (cut, through all)
    with BuildSketch(Plane(origin=(0, 20, 0), x_dir=(1, 0, 0), z_dir=(0, 1, 0))):
        with Locations((70, 20)):
            Rectangle(SKETCH8_W, SKETCH8_H)
    extrude(amount=-CUT_EXTRUDE1_DEPTH, mode=Mode.SUBTRACT)


solid = Compound([body_2.part, body_3.part, body_4.part, body_5.part, part_1.part, body_6.part])
